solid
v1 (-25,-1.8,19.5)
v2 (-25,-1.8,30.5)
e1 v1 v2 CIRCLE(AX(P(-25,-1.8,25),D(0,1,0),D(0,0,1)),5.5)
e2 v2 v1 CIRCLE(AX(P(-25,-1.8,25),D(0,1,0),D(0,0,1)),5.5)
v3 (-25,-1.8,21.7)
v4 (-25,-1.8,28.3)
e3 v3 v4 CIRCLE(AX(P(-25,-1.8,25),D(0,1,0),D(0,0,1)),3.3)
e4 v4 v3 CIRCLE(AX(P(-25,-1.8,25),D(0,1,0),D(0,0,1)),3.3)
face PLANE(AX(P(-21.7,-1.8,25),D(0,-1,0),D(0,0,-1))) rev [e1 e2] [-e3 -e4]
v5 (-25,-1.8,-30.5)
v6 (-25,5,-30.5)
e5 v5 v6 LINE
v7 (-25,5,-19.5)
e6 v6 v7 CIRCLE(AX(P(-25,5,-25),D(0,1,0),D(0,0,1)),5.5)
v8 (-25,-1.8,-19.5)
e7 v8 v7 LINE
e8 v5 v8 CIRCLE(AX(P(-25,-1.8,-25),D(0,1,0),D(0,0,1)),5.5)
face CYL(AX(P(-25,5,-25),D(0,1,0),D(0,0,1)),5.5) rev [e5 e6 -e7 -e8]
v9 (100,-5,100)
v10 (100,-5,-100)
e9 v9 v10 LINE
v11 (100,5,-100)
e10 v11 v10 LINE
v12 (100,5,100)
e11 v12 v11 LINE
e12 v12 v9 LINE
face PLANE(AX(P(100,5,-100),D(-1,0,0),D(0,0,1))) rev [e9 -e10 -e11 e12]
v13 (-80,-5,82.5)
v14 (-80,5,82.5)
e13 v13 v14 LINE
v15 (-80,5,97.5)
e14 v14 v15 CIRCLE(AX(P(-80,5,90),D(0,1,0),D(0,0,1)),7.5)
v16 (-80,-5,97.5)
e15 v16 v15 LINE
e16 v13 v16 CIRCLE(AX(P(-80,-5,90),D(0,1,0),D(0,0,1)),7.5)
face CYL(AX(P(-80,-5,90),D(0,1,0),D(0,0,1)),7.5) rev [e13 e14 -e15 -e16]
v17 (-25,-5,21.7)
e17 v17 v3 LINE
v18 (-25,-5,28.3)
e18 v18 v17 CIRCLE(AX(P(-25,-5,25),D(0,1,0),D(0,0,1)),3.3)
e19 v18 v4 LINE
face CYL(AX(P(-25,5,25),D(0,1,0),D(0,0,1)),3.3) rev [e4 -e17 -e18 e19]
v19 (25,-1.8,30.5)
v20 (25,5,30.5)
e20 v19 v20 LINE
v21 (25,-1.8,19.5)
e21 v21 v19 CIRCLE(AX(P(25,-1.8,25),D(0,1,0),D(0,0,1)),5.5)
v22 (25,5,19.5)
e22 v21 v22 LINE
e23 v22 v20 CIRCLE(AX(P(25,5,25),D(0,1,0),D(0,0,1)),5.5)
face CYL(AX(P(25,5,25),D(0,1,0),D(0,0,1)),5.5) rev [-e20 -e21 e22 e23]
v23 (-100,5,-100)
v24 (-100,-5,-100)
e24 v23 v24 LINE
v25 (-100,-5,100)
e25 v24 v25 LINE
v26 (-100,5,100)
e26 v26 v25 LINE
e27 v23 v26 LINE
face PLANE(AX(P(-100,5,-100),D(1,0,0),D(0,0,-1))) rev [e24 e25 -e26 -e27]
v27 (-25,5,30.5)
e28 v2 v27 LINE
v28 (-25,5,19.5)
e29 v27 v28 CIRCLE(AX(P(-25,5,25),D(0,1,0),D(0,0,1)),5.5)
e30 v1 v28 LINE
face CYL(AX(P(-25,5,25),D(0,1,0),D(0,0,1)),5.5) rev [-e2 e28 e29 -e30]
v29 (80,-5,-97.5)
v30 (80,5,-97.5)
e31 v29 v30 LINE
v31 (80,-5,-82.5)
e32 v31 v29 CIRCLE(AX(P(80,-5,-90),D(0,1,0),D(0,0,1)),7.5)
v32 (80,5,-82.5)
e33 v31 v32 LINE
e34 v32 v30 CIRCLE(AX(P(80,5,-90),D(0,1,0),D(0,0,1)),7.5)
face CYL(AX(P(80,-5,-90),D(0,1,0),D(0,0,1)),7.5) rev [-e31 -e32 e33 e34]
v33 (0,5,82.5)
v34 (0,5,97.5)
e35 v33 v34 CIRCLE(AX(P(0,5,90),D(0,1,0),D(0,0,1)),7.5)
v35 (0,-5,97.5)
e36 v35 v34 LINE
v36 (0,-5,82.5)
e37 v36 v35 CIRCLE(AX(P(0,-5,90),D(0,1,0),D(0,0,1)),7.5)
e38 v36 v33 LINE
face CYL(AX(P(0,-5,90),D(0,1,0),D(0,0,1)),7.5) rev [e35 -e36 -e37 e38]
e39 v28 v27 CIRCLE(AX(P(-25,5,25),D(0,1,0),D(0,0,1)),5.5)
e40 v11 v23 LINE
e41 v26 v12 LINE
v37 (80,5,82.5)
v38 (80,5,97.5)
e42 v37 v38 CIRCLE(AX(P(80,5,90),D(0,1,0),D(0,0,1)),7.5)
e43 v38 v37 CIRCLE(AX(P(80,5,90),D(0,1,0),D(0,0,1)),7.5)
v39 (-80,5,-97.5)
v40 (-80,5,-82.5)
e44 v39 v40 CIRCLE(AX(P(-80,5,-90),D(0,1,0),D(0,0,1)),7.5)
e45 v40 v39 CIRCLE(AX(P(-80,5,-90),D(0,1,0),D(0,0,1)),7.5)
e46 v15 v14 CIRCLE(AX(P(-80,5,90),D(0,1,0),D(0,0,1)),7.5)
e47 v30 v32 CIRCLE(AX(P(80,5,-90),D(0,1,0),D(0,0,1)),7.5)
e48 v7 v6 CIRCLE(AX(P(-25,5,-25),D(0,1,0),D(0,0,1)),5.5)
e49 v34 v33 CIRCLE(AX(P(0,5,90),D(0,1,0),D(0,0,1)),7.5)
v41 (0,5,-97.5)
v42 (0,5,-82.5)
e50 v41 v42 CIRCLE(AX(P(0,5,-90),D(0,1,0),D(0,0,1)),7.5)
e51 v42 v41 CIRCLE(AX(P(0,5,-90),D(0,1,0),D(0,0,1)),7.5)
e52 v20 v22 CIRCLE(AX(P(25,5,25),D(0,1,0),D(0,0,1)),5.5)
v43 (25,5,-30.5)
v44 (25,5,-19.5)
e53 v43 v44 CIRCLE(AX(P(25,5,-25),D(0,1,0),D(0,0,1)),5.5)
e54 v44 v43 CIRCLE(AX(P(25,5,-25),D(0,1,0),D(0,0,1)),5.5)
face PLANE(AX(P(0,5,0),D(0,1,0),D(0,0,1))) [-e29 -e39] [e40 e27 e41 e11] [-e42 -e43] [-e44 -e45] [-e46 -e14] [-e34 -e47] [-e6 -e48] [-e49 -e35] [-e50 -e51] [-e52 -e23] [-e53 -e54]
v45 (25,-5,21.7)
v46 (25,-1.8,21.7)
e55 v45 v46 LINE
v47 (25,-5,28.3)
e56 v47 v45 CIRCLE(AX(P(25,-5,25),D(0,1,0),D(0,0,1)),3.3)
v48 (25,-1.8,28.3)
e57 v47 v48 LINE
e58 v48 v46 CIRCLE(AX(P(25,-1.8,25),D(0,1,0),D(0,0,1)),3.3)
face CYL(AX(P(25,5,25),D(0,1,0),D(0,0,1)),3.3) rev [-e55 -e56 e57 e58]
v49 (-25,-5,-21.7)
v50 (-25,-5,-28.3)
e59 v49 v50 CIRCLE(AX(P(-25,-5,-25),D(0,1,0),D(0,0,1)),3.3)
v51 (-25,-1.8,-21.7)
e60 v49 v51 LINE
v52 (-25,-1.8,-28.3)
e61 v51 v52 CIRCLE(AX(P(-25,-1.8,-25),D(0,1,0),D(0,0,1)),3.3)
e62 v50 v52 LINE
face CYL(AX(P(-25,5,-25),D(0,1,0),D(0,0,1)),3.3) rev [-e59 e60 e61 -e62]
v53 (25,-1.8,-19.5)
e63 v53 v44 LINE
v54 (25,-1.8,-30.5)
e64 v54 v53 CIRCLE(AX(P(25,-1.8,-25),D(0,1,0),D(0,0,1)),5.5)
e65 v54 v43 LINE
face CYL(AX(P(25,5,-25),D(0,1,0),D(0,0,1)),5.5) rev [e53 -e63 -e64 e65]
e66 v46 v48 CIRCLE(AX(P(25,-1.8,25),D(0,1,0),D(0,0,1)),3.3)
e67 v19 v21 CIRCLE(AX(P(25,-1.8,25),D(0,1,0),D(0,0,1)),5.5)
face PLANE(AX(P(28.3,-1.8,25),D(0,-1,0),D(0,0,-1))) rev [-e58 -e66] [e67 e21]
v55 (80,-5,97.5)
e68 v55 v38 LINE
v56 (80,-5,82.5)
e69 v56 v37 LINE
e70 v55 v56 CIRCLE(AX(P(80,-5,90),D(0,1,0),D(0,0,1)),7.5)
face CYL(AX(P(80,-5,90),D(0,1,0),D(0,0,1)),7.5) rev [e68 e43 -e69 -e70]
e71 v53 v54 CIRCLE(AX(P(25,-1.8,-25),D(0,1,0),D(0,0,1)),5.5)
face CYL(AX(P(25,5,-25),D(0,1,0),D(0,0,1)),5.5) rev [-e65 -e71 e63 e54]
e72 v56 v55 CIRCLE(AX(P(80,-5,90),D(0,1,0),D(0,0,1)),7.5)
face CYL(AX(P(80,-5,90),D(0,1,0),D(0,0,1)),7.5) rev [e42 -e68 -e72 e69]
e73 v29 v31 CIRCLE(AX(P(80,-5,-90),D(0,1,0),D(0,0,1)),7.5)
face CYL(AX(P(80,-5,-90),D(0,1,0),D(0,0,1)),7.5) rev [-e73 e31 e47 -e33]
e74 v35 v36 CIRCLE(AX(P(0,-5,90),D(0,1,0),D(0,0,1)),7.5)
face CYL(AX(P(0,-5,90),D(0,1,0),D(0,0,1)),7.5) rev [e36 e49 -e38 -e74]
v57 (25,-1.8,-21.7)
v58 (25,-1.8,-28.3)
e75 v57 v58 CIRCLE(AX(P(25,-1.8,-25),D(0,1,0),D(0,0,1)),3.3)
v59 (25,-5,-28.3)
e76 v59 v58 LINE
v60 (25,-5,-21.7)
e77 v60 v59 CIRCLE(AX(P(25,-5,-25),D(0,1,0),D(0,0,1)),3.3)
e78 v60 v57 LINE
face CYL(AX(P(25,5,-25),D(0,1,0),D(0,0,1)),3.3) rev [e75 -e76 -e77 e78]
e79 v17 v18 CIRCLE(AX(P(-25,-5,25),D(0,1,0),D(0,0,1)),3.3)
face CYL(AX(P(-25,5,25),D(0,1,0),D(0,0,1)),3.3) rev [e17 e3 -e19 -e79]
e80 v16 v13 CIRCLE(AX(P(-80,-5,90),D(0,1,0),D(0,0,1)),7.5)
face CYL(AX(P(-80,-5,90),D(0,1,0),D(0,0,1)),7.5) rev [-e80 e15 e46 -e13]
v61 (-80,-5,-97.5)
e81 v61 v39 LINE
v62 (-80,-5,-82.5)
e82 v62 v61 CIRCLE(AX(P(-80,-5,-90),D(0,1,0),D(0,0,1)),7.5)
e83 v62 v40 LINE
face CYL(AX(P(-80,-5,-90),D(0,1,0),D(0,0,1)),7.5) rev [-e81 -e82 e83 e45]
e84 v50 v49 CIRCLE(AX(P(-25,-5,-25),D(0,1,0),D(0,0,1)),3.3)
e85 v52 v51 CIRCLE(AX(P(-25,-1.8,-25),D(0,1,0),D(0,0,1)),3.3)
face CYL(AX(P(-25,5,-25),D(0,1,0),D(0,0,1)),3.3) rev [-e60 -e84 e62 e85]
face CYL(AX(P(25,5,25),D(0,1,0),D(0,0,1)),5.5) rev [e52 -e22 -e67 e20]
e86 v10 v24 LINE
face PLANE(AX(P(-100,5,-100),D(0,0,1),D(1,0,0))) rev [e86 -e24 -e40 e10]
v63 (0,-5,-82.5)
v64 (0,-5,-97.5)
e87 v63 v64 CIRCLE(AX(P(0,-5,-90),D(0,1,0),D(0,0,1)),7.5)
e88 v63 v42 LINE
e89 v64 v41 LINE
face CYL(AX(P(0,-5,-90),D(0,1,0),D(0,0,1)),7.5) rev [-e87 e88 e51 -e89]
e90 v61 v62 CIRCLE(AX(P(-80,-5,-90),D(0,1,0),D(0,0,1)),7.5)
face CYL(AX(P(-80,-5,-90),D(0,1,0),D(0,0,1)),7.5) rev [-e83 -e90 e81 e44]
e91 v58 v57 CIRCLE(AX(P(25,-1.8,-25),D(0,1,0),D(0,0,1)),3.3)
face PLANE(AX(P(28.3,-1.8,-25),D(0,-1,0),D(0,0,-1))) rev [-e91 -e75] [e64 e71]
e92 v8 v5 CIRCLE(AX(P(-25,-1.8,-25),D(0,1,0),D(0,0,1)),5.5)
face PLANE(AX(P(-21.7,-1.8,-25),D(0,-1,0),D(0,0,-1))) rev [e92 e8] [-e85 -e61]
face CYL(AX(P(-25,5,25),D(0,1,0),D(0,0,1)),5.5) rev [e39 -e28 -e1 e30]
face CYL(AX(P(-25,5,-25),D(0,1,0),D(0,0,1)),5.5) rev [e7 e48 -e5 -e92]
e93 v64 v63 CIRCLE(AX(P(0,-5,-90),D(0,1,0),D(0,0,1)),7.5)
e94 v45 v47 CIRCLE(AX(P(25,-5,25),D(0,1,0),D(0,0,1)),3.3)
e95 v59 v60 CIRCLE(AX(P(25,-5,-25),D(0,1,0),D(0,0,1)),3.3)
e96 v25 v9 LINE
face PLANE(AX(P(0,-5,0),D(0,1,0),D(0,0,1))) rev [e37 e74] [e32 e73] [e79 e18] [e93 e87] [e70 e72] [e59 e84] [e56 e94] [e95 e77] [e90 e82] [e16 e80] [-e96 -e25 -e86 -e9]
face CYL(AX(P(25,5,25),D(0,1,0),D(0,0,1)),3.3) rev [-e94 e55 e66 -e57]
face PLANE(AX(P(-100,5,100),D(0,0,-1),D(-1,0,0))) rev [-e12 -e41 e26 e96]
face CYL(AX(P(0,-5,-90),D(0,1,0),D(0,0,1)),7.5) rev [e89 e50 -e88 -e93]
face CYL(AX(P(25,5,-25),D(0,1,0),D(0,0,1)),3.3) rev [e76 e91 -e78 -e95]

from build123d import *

# Parameters (mm, degrees)
SKETCH1_W                                           = 200
SKETCH1_H                                           = 200
BOSS_EXTRUDE1_DEPTH                                 = 5
SKETCH2_R                                           = 7.5
CUT_EXTRUDE1_DEPTH                                  = 10
LPATTERN1_COUNT                                     = 2
LPATTERN1_PITCH                                     = 180
LPATTERN1_COUNT_DIR2                                = 3
LPATTERN1_PITCH_DIR2                                = 80
HOLE_SIZE_BASED_ON_SOCKET_HEAD_CAP_SCRE_D           = 6.6
HOLE_SIZE_BASED_ON_SOCKET_HEAD_CAP_SCRE_CBORE_D     = 11
HOLE_SIZE_BASED_ON_SOCKET_HEAD_CAP_SCRE_CBORE_DEPTH = 6.8


with BuildPart() as part:
    # Sketch1 → Boss-Extrude1 (new, symmetric)
    with BuildSketch(Plane(origin=(0, 0, 0), x_dir=(1, 0, 0), z_dir=(0, 1, 0))):
        Rectangle(SKETCH1_W, SKETCH1_H)
    extrude(amount=BOSS_EXTRUDE1_DEPTH, both=True)

    # Sketch2 → Cut-Extrude1 (cut)
    with BuildSketch(Plane(origin=(0, 5, 0), x_dir=(1, 0, 0), z_dir=(0, 1, 0))):
        with Locations(Location((80, 90, 0), (0, 0, 270))):
            Circle(SKETCH2_R)
    cut_extrude1 = extrude(amount=-CUT_EXTRUDE1_DEPTH, mode=Mode.SUBTRACT)

    # LPattern1: Cut-Extrude1 2 × 3
    with Locations(*[(-j * LPATTERN1_PITCH_DIR2, 0, i * LPATTERN1_PITCH) for i in range(LPATTERN1_COUNT) for j in range(LPATTERN1_COUNT_DIR2) if (i, j) != (0, 0)]):
        add(cut_extrude1, mode=Mode.SUBTRACT)

    # Hole Size (based on socket head cap screw type)1 (through all)
    with Locations(Plane(origin=(0, 5, 0), x_dir=(1, 0, 0), z_dir=(0, 1, 0))):
        with Locations((25, 25), (25, -25), (-25, 25), (-25, -25)):
            CounterBoreHole(HOLE_SIZE_BASED_ON_SOCKET_HEAD_CAP_SCRE_D / 2, HOLE_SIZE_BASED_ON_SOCKET_HEAD_CAP_SCRE_CBORE_D / 2, HOLE_SIZE_BASED_ON_SOCKET_HEAD_CAP_SCRE_CBORE_DEPTH)


solid = part.part
